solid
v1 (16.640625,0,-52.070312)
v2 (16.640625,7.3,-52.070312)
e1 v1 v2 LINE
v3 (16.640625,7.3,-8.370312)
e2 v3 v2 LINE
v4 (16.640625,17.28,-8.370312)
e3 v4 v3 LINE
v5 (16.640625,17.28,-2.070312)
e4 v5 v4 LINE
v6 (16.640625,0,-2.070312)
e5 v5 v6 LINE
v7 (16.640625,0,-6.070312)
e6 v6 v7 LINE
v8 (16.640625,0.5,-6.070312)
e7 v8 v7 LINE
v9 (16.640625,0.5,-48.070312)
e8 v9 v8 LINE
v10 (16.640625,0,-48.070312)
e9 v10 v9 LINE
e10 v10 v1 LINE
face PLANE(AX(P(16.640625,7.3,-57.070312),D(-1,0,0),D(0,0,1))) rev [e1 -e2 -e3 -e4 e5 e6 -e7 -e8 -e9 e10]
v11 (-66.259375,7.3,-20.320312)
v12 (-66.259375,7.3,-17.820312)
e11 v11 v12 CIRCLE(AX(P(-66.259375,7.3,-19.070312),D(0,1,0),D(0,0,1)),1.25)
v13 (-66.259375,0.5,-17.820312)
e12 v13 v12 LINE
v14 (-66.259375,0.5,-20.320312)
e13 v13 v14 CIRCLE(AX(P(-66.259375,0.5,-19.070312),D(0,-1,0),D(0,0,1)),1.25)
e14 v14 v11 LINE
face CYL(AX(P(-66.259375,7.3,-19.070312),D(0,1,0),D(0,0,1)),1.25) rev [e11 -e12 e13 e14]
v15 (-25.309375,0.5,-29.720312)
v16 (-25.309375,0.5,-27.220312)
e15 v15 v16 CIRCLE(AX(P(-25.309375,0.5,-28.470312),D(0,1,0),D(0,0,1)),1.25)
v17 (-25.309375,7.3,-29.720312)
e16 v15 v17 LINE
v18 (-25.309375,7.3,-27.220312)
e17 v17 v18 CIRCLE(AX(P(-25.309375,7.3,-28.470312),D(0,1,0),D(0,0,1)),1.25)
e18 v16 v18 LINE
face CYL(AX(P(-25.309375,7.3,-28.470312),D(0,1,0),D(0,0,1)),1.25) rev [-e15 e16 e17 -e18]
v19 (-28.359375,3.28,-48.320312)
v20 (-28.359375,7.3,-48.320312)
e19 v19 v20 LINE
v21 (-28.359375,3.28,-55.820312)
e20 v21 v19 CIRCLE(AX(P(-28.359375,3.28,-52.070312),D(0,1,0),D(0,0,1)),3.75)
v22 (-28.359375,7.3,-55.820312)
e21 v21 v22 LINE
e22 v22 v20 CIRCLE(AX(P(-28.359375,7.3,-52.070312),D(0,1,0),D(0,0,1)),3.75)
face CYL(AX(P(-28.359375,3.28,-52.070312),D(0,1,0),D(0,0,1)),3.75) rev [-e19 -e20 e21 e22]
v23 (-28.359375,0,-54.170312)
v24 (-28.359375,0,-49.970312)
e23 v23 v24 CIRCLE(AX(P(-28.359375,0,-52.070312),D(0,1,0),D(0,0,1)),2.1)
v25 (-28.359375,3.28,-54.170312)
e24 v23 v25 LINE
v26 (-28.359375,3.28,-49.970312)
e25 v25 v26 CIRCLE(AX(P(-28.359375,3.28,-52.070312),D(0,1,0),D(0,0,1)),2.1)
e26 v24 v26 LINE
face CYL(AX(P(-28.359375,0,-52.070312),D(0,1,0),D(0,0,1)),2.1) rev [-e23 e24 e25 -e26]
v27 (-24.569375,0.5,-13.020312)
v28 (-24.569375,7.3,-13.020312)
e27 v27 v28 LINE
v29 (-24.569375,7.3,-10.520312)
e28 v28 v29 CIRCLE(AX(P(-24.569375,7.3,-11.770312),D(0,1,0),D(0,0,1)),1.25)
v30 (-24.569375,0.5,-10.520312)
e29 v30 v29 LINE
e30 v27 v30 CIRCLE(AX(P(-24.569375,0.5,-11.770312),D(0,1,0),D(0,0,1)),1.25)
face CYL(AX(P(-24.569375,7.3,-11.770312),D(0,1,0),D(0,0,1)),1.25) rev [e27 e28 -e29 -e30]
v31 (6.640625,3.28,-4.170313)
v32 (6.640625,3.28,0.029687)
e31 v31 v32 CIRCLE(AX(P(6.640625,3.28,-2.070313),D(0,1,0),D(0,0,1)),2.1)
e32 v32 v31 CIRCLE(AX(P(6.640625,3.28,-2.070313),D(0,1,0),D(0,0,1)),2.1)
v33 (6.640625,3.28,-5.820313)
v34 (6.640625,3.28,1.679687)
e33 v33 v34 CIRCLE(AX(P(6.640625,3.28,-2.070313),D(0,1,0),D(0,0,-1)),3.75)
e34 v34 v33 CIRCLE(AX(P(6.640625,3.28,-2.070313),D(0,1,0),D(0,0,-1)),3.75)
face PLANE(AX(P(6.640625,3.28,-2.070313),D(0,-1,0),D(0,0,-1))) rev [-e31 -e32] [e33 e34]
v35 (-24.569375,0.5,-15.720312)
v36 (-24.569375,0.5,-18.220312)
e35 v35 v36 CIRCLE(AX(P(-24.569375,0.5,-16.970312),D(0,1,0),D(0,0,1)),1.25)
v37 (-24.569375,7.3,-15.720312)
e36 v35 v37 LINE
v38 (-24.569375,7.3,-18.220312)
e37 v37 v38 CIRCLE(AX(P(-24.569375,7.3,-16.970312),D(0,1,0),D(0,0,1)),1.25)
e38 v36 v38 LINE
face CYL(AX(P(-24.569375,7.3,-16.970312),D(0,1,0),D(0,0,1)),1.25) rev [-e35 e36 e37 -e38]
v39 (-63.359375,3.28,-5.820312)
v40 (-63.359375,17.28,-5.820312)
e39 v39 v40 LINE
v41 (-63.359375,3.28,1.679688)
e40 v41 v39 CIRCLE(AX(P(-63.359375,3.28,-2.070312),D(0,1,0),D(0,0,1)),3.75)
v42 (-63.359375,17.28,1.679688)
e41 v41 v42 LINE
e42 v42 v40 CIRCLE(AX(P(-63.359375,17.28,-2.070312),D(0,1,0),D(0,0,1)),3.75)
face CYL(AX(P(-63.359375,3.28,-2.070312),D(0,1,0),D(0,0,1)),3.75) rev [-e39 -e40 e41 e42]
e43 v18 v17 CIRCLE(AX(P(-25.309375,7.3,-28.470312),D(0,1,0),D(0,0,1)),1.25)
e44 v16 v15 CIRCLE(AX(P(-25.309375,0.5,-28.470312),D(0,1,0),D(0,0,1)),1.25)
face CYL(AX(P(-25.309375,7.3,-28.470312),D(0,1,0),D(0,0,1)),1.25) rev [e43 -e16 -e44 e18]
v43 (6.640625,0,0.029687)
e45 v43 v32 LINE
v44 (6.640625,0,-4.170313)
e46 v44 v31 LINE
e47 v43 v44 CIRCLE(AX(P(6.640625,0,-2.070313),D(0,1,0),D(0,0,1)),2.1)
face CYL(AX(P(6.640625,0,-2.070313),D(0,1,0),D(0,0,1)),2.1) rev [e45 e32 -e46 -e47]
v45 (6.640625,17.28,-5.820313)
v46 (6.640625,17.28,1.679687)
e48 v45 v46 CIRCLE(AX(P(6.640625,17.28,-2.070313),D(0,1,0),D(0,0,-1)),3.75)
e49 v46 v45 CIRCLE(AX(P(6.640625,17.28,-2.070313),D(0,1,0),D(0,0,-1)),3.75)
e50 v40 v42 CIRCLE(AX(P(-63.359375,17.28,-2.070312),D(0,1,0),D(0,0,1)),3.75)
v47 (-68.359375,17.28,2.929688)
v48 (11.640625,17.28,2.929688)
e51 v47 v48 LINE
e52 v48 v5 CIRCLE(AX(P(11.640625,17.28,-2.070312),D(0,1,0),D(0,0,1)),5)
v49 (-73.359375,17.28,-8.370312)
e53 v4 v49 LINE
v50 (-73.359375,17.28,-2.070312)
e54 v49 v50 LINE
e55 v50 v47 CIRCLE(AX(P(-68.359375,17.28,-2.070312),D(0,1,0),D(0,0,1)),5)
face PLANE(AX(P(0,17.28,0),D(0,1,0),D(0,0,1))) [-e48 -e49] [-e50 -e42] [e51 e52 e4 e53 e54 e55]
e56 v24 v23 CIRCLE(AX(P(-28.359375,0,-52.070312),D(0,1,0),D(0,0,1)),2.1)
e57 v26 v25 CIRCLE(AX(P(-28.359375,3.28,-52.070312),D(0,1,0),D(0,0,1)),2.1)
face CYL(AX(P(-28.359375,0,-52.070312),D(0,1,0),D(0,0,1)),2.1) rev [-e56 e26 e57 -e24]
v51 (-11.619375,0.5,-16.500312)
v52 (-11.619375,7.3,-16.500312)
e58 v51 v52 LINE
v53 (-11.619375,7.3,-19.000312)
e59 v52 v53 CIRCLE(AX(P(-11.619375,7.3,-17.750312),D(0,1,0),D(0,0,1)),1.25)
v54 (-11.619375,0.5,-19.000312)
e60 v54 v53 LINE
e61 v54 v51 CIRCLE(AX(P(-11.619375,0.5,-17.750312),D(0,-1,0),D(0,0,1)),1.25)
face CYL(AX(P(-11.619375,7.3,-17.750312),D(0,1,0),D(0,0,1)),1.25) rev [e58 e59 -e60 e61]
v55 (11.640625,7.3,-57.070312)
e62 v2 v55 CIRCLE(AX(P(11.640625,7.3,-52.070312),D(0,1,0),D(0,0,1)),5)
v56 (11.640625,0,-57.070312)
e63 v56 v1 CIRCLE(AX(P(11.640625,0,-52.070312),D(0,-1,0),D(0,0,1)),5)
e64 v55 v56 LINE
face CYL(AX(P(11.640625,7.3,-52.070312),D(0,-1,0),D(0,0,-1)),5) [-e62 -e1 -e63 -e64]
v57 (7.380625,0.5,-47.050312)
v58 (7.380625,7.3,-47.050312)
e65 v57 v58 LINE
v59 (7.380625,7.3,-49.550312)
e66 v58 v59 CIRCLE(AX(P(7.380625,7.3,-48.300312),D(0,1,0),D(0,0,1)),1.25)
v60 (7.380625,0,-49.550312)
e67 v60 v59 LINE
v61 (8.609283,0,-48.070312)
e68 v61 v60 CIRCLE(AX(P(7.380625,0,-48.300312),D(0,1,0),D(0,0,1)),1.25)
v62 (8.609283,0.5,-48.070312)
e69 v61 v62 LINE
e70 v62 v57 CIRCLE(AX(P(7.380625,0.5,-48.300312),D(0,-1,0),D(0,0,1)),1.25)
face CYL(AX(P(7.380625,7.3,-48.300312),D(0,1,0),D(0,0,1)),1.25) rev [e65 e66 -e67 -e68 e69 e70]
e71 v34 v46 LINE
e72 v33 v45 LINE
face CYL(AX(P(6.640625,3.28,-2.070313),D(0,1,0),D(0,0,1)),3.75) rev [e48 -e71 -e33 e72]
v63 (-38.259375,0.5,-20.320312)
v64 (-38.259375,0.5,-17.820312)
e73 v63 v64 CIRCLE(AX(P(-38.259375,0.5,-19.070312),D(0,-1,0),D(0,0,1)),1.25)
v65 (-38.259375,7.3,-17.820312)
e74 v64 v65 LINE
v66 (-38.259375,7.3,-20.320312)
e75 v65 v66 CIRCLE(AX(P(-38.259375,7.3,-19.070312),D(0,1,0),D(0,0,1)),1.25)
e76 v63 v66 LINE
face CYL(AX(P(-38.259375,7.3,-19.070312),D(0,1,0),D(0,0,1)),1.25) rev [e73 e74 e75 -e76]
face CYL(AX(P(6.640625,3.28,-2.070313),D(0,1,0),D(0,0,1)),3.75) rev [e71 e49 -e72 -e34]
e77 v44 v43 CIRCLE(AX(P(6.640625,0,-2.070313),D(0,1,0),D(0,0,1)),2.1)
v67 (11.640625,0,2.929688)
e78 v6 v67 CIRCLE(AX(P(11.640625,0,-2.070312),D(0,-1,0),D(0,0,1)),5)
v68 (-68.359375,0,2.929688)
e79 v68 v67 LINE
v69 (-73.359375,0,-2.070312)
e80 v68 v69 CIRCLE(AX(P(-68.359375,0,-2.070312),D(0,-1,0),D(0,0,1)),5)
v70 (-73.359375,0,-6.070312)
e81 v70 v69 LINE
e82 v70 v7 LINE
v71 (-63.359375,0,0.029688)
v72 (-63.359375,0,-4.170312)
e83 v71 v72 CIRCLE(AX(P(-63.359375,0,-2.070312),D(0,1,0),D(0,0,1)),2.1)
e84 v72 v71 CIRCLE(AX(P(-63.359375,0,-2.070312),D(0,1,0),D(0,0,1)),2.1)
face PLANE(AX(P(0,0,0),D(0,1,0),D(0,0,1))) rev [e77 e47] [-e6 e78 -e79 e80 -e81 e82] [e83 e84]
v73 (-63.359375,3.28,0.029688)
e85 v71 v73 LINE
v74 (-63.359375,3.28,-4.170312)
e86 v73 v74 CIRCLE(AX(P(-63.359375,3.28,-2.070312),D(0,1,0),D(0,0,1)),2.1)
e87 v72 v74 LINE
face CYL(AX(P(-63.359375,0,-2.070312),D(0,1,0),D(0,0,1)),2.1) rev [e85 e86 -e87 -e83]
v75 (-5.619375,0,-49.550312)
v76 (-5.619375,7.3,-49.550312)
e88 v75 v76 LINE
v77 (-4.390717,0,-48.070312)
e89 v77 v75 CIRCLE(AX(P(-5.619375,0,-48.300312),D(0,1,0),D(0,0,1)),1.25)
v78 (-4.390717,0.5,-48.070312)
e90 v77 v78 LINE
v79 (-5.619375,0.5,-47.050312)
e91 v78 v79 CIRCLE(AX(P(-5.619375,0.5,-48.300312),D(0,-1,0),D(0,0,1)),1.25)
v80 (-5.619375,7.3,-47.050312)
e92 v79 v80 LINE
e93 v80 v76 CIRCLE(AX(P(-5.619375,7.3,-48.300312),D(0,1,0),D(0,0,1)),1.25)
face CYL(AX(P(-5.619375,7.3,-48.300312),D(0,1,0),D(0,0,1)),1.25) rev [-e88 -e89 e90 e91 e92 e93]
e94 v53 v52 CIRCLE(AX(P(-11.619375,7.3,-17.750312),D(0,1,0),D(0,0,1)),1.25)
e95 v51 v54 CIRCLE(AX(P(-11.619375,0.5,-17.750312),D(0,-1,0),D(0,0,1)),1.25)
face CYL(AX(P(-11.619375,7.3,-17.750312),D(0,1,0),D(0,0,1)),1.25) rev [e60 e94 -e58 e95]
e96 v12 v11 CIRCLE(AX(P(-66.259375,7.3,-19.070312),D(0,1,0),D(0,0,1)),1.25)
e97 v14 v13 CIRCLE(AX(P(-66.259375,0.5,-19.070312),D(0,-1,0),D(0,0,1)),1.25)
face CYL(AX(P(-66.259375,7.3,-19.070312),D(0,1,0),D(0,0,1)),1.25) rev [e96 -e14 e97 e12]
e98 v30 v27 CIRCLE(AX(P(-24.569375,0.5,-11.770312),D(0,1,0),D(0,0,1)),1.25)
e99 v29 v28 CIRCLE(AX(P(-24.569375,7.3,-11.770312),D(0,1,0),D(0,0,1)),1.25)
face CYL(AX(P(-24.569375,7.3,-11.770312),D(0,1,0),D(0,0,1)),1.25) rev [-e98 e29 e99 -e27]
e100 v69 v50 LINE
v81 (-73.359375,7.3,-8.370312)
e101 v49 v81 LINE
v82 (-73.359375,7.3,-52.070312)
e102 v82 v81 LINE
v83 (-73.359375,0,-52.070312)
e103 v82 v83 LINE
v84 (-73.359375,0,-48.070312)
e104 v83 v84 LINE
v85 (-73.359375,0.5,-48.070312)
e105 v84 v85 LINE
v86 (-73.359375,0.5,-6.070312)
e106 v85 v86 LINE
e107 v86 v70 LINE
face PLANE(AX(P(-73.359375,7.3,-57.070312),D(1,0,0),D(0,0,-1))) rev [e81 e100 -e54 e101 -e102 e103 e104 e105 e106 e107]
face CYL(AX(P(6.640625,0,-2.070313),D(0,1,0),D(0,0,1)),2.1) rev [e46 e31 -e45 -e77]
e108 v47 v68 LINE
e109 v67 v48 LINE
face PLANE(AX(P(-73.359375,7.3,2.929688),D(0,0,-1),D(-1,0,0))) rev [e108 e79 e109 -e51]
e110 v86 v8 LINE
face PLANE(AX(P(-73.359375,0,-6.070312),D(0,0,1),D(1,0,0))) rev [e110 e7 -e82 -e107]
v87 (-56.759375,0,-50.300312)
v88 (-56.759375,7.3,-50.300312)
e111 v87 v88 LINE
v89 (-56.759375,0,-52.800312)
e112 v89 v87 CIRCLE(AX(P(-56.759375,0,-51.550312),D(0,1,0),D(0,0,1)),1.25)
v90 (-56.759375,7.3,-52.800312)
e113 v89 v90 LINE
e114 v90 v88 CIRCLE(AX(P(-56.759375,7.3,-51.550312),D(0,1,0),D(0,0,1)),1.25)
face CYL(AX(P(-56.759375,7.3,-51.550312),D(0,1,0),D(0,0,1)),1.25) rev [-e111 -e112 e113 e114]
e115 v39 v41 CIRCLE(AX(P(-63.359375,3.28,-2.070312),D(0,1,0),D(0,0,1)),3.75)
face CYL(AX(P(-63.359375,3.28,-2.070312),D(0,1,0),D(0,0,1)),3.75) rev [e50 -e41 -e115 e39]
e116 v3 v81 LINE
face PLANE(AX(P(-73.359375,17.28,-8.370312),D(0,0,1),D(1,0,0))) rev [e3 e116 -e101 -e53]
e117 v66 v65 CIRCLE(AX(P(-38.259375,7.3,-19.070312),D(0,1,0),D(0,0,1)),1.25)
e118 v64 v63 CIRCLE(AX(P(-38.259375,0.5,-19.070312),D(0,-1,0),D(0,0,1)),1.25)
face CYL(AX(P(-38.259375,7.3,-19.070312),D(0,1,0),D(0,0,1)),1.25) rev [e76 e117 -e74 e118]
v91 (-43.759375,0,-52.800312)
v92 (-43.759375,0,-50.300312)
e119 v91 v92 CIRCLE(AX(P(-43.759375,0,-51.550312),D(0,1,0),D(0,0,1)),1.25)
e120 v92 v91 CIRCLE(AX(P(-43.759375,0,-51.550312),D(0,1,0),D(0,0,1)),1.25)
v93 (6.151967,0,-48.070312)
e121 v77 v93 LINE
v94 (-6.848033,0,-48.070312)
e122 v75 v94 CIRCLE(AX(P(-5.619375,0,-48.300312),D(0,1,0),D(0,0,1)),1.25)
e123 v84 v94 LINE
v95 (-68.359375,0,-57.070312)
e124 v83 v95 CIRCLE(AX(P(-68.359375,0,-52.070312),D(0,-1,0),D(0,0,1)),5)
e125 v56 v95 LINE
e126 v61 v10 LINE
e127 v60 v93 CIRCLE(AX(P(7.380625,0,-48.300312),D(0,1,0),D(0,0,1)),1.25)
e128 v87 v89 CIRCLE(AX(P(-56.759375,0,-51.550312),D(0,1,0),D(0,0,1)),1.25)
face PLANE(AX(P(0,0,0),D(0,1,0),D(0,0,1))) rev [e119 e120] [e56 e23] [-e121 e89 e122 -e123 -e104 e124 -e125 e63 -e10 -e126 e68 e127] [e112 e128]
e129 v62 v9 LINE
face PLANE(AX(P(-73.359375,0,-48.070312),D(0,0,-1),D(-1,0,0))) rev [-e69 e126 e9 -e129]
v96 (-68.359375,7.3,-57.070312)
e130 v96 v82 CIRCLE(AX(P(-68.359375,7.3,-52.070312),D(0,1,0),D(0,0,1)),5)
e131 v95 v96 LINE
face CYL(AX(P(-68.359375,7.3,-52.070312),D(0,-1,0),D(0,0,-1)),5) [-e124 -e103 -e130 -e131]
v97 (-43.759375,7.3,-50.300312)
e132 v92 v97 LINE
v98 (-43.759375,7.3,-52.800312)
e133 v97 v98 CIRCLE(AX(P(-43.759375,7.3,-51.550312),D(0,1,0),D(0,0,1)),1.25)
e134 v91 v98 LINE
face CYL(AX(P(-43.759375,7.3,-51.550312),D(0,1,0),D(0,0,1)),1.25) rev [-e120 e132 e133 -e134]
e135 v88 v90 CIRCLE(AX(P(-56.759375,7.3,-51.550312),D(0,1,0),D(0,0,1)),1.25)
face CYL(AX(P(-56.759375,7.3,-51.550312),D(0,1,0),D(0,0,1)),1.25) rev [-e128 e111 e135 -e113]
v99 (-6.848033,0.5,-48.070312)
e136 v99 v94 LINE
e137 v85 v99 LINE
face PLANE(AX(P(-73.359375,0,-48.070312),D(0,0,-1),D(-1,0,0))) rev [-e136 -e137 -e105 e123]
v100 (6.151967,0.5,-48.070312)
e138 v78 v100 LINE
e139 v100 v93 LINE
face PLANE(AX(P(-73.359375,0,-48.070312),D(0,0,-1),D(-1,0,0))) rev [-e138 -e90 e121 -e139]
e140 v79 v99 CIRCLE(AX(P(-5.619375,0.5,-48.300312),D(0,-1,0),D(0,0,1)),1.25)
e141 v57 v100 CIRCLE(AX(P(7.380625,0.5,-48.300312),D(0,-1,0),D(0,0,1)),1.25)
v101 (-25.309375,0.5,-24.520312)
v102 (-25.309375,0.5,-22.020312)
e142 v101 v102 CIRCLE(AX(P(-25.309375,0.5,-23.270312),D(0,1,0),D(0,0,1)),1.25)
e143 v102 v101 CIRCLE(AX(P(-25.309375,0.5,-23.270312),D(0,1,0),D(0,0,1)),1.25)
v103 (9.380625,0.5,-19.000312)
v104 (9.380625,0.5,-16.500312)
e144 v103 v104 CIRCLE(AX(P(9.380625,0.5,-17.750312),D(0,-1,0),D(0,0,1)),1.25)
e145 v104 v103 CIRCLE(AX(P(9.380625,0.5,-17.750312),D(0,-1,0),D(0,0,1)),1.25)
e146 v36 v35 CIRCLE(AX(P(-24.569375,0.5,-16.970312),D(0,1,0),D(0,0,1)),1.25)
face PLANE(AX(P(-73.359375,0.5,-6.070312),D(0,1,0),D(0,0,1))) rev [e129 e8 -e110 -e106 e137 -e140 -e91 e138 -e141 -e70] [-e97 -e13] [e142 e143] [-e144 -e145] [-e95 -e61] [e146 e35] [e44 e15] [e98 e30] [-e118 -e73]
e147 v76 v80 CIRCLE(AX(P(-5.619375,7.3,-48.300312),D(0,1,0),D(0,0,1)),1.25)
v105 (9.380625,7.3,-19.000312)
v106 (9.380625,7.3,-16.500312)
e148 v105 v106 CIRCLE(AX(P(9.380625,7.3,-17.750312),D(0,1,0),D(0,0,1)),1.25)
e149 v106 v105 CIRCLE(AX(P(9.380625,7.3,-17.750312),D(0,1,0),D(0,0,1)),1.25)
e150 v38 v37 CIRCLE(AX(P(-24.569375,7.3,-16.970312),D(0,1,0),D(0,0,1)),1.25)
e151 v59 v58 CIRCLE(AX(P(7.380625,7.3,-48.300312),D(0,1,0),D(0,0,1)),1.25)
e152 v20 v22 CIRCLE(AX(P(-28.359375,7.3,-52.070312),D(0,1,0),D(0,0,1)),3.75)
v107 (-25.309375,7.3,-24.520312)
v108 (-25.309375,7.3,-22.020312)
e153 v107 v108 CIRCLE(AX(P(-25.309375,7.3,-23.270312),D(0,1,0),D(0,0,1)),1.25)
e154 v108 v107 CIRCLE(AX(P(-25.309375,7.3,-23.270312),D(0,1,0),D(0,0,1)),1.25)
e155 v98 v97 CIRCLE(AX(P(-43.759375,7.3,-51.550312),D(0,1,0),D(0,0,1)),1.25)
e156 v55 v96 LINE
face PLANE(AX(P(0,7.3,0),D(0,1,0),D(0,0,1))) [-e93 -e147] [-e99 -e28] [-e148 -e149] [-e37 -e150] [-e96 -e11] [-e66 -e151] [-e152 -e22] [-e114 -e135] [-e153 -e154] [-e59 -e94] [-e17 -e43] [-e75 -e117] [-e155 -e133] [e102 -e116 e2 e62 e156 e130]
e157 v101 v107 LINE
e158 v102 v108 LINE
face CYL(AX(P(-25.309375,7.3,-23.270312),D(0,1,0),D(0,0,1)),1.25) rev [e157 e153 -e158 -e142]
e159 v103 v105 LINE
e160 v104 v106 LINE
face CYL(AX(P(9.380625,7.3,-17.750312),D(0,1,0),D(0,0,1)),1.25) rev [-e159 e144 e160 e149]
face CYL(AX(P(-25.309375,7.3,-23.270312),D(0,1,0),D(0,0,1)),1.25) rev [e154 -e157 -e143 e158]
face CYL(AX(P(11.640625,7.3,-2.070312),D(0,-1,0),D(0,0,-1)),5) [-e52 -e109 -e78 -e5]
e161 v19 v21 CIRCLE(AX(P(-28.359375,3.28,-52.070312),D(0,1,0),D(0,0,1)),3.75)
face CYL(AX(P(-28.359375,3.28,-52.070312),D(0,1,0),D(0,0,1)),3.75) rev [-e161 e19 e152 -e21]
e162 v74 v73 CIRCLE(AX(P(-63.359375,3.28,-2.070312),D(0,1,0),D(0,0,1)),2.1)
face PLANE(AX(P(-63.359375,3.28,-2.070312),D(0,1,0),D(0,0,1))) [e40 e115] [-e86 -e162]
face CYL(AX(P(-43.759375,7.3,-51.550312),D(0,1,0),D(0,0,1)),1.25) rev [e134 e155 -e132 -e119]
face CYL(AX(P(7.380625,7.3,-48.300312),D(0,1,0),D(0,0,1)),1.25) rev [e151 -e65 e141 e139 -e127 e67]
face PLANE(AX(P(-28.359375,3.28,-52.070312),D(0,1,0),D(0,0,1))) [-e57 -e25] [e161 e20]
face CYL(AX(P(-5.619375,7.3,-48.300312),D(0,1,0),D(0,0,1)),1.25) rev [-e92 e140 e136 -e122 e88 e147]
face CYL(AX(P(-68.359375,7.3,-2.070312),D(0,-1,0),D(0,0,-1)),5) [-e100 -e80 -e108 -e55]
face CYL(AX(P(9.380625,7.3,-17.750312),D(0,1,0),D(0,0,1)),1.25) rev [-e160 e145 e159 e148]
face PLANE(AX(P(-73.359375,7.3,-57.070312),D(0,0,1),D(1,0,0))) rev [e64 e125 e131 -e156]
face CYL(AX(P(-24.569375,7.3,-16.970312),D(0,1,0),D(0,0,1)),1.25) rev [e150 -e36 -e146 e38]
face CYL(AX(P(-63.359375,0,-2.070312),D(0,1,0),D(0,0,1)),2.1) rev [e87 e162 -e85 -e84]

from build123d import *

# Parameters (mm, degrees)
SKETCH1_W             = 90
SKETCH1_H             = 60
BOSS_EXTRUDE1_DEPTH   = 7.3
SKETCH2_W             = 90
SKETCH2_H             = 11.3
BOSS_EXTRUDE2_DEPTH   = 9.98
M3_TAPPED_HOLE1_D     = 2.5
M3_TAPPED_HOLE1_DEPTH = 7.5
M3_TAPPED_HOLE1_TIP   = 0.751075774
FILLET1_R             = 5
SKETCH5_R             = 3.75
CUT_EXTRUDE1_DEPTH    = 14
SKETCH6_R             = 2.1
CUT_EXTRUDE2_DEPTH    = 94.992651145
SKETCH7_W             = 42
SKETCH7_H             = 0.5
CUT_EXTRUDE3_DEPTH    = 108.961191957
M3_TAPPED_HOLE3_D     = 2.5
M3_TAPPED_HOLE3_DEPTH = 8.5
M3_TAPPED_HOLE3_TIP   = 0.751075774


with BuildPart() as part:
    # Sketch1 → Boss-Extrude1 (new body)
    with BuildSketch(Plane(origin=(0, 0, 0), x_dir=(1, 0, 0), z_dir=(0, 1, 0))):
        with Locations((-28.359375, 27.0703125)):
            Rectangle(SKETCH1_W, SKETCH1_H)
    extrude(amount=BOSS_EXTRUDE1_DEPTH)

    # Sketch2 → Boss-Extrude2 (add)
    with BuildSketch(Plane(origin=(0, 7.3, 0), x_dir=(1, 0, 0), z_dir=(0, 1, 0))):
        with Locations((-28.359375, 2.7203125)):
            Rectangle(SKETCH2_W, SKETCH2_H)
    extrude(amount=BOSS_EXTRUDE2_DEPTH)

    # M3 Tapped Hole1
    with Locations(Plane(origin=(0, 7.3, 0), x_dir=(1, 0, 0), z_dir=(0, 1, 0))):
        with Locations((-66.259375, 19.0703125), (-38.259375, 19.0703125), (-56.759375, 51.5503125), (-43.759375, 51.5503125), (-5.619375, 48.3003125), (7.380625, 48.3003125), (-11.619375, 17.7503125), (9.380625, 17.7503125)):
            Hole(M3_TAPPED_HOLE1_D / 2, depth=M3_TAPPED_HOLE1_DEPTH)
            with Locations((0, 0, -(M3_TAPPED_HOLE1_DEPTH + M3_TAPPED_HOLE1_TIP / 2))):  # 118° drill point
                Cone(0, M3_TAPPED_HOLE1_D / 2, M3_TAPPED_HOLE1_TIP, mode=Mode.SUBTRACT)

    # Fillet1
    fillet1_edges = [part.edges().sort_by_distance(p)[0] for p in [
        (-73.359375, 3.65, -57.0703125),
        (16.640625, 3.65, -57.0703125),
        (16.640625, 8.64, 2.9296875),
        (-73.359375, 8.64, 2.9296875),
    ]]
    fillet(fillet1_edges, radius=FILLET1_R)

    # Sketch5 → Cut-Extrude1 (cut)
    with BuildSketch(Plane(origin=(0, 17.28, 0), x_dir=(1, 0, 0), z_dir=(0, 1, 0))):
        with Locations(Location((-28.359375, 52.0703125, 0), (0, 0, 270))):
            Circle(SKETCH5_R)
        with Locations(Location((-63.359375, 2.0703125, 0), (0, 0, 270))):
            Circle(SKETCH5_R)
        with Locations(Location((6.640625, 2.0703125, 0), (0, 0, 90))):
            Circle(SKETCH5_R)
    extrude(amount=-CUT_EXTRUDE1_DEPTH, mode=Mode.SUBTRACT)

    # Sketch6 → Cut-Extrude2 (cut, through all)
    with BuildSketch(Plane(origin=(0, 3.28, 0), x_dir=(1, 0, 0), z_dir=(0, 1, 0))):
        with Locations(Location((-28.359375, 52.0703125, 0), (0, 0, 270))):
            Circle(SKETCH6_R)
        with Locations(Location((-63.359375, 2.0703125, 0), (0, 0, 270))):
            Circle(SKETCH6_R)
        with Locations(Location((6.640625, 2.0703125, 0), (0, 0, 270))):
            Circle(SKETCH6_R)
    extrude(amount=-CUT_EXTRUDE2_DEPTH, mode=Mode.SUBTRACT)

    # Sketch7 → Cut-Extrude3 (cut, through all)
    with BuildSketch(Plane(origin=(16.640625, 0, 0), x_dir=(0, 0, -1), z_dir=(1, 0, 0))):
        with Locations((27.0703125, 0.25)):
            Rectangle(SKETCH7_W, SKETCH7_H)
    extrude(amount=-CUT_EXTRUDE3_DEPTH, mode=Mode.SUBTRACT)

    # M3 Tapped Hole3
    with Locations(Plane(origin=(0, 7.3, 0), x_dir=(1, 0, 0), z_dir=(0, 1, 0))):
        with Locations((-24.569375, 11.7703125), (-24.569375, 16.9703125), (-25.309375, 23.2703125), (-25.309375, 28.4703125)):
            Hole(M3_TAPPED_HOLE3_D / 2, depth=M3_TAPPED_HOLE3_DEPTH)
            with Locations((0, 0, -(M3_TAPPED_HOLE3_DEPTH + M3_TAPPED_HOLE3_TIP / 2))):  # 118° drill point
                Cone(0, M3_TAPPED_HOLE3_D / 2, M3_TAPPED_HOLE3_TIP, mode=Mode.SUBTRACT)


solid = part.part
